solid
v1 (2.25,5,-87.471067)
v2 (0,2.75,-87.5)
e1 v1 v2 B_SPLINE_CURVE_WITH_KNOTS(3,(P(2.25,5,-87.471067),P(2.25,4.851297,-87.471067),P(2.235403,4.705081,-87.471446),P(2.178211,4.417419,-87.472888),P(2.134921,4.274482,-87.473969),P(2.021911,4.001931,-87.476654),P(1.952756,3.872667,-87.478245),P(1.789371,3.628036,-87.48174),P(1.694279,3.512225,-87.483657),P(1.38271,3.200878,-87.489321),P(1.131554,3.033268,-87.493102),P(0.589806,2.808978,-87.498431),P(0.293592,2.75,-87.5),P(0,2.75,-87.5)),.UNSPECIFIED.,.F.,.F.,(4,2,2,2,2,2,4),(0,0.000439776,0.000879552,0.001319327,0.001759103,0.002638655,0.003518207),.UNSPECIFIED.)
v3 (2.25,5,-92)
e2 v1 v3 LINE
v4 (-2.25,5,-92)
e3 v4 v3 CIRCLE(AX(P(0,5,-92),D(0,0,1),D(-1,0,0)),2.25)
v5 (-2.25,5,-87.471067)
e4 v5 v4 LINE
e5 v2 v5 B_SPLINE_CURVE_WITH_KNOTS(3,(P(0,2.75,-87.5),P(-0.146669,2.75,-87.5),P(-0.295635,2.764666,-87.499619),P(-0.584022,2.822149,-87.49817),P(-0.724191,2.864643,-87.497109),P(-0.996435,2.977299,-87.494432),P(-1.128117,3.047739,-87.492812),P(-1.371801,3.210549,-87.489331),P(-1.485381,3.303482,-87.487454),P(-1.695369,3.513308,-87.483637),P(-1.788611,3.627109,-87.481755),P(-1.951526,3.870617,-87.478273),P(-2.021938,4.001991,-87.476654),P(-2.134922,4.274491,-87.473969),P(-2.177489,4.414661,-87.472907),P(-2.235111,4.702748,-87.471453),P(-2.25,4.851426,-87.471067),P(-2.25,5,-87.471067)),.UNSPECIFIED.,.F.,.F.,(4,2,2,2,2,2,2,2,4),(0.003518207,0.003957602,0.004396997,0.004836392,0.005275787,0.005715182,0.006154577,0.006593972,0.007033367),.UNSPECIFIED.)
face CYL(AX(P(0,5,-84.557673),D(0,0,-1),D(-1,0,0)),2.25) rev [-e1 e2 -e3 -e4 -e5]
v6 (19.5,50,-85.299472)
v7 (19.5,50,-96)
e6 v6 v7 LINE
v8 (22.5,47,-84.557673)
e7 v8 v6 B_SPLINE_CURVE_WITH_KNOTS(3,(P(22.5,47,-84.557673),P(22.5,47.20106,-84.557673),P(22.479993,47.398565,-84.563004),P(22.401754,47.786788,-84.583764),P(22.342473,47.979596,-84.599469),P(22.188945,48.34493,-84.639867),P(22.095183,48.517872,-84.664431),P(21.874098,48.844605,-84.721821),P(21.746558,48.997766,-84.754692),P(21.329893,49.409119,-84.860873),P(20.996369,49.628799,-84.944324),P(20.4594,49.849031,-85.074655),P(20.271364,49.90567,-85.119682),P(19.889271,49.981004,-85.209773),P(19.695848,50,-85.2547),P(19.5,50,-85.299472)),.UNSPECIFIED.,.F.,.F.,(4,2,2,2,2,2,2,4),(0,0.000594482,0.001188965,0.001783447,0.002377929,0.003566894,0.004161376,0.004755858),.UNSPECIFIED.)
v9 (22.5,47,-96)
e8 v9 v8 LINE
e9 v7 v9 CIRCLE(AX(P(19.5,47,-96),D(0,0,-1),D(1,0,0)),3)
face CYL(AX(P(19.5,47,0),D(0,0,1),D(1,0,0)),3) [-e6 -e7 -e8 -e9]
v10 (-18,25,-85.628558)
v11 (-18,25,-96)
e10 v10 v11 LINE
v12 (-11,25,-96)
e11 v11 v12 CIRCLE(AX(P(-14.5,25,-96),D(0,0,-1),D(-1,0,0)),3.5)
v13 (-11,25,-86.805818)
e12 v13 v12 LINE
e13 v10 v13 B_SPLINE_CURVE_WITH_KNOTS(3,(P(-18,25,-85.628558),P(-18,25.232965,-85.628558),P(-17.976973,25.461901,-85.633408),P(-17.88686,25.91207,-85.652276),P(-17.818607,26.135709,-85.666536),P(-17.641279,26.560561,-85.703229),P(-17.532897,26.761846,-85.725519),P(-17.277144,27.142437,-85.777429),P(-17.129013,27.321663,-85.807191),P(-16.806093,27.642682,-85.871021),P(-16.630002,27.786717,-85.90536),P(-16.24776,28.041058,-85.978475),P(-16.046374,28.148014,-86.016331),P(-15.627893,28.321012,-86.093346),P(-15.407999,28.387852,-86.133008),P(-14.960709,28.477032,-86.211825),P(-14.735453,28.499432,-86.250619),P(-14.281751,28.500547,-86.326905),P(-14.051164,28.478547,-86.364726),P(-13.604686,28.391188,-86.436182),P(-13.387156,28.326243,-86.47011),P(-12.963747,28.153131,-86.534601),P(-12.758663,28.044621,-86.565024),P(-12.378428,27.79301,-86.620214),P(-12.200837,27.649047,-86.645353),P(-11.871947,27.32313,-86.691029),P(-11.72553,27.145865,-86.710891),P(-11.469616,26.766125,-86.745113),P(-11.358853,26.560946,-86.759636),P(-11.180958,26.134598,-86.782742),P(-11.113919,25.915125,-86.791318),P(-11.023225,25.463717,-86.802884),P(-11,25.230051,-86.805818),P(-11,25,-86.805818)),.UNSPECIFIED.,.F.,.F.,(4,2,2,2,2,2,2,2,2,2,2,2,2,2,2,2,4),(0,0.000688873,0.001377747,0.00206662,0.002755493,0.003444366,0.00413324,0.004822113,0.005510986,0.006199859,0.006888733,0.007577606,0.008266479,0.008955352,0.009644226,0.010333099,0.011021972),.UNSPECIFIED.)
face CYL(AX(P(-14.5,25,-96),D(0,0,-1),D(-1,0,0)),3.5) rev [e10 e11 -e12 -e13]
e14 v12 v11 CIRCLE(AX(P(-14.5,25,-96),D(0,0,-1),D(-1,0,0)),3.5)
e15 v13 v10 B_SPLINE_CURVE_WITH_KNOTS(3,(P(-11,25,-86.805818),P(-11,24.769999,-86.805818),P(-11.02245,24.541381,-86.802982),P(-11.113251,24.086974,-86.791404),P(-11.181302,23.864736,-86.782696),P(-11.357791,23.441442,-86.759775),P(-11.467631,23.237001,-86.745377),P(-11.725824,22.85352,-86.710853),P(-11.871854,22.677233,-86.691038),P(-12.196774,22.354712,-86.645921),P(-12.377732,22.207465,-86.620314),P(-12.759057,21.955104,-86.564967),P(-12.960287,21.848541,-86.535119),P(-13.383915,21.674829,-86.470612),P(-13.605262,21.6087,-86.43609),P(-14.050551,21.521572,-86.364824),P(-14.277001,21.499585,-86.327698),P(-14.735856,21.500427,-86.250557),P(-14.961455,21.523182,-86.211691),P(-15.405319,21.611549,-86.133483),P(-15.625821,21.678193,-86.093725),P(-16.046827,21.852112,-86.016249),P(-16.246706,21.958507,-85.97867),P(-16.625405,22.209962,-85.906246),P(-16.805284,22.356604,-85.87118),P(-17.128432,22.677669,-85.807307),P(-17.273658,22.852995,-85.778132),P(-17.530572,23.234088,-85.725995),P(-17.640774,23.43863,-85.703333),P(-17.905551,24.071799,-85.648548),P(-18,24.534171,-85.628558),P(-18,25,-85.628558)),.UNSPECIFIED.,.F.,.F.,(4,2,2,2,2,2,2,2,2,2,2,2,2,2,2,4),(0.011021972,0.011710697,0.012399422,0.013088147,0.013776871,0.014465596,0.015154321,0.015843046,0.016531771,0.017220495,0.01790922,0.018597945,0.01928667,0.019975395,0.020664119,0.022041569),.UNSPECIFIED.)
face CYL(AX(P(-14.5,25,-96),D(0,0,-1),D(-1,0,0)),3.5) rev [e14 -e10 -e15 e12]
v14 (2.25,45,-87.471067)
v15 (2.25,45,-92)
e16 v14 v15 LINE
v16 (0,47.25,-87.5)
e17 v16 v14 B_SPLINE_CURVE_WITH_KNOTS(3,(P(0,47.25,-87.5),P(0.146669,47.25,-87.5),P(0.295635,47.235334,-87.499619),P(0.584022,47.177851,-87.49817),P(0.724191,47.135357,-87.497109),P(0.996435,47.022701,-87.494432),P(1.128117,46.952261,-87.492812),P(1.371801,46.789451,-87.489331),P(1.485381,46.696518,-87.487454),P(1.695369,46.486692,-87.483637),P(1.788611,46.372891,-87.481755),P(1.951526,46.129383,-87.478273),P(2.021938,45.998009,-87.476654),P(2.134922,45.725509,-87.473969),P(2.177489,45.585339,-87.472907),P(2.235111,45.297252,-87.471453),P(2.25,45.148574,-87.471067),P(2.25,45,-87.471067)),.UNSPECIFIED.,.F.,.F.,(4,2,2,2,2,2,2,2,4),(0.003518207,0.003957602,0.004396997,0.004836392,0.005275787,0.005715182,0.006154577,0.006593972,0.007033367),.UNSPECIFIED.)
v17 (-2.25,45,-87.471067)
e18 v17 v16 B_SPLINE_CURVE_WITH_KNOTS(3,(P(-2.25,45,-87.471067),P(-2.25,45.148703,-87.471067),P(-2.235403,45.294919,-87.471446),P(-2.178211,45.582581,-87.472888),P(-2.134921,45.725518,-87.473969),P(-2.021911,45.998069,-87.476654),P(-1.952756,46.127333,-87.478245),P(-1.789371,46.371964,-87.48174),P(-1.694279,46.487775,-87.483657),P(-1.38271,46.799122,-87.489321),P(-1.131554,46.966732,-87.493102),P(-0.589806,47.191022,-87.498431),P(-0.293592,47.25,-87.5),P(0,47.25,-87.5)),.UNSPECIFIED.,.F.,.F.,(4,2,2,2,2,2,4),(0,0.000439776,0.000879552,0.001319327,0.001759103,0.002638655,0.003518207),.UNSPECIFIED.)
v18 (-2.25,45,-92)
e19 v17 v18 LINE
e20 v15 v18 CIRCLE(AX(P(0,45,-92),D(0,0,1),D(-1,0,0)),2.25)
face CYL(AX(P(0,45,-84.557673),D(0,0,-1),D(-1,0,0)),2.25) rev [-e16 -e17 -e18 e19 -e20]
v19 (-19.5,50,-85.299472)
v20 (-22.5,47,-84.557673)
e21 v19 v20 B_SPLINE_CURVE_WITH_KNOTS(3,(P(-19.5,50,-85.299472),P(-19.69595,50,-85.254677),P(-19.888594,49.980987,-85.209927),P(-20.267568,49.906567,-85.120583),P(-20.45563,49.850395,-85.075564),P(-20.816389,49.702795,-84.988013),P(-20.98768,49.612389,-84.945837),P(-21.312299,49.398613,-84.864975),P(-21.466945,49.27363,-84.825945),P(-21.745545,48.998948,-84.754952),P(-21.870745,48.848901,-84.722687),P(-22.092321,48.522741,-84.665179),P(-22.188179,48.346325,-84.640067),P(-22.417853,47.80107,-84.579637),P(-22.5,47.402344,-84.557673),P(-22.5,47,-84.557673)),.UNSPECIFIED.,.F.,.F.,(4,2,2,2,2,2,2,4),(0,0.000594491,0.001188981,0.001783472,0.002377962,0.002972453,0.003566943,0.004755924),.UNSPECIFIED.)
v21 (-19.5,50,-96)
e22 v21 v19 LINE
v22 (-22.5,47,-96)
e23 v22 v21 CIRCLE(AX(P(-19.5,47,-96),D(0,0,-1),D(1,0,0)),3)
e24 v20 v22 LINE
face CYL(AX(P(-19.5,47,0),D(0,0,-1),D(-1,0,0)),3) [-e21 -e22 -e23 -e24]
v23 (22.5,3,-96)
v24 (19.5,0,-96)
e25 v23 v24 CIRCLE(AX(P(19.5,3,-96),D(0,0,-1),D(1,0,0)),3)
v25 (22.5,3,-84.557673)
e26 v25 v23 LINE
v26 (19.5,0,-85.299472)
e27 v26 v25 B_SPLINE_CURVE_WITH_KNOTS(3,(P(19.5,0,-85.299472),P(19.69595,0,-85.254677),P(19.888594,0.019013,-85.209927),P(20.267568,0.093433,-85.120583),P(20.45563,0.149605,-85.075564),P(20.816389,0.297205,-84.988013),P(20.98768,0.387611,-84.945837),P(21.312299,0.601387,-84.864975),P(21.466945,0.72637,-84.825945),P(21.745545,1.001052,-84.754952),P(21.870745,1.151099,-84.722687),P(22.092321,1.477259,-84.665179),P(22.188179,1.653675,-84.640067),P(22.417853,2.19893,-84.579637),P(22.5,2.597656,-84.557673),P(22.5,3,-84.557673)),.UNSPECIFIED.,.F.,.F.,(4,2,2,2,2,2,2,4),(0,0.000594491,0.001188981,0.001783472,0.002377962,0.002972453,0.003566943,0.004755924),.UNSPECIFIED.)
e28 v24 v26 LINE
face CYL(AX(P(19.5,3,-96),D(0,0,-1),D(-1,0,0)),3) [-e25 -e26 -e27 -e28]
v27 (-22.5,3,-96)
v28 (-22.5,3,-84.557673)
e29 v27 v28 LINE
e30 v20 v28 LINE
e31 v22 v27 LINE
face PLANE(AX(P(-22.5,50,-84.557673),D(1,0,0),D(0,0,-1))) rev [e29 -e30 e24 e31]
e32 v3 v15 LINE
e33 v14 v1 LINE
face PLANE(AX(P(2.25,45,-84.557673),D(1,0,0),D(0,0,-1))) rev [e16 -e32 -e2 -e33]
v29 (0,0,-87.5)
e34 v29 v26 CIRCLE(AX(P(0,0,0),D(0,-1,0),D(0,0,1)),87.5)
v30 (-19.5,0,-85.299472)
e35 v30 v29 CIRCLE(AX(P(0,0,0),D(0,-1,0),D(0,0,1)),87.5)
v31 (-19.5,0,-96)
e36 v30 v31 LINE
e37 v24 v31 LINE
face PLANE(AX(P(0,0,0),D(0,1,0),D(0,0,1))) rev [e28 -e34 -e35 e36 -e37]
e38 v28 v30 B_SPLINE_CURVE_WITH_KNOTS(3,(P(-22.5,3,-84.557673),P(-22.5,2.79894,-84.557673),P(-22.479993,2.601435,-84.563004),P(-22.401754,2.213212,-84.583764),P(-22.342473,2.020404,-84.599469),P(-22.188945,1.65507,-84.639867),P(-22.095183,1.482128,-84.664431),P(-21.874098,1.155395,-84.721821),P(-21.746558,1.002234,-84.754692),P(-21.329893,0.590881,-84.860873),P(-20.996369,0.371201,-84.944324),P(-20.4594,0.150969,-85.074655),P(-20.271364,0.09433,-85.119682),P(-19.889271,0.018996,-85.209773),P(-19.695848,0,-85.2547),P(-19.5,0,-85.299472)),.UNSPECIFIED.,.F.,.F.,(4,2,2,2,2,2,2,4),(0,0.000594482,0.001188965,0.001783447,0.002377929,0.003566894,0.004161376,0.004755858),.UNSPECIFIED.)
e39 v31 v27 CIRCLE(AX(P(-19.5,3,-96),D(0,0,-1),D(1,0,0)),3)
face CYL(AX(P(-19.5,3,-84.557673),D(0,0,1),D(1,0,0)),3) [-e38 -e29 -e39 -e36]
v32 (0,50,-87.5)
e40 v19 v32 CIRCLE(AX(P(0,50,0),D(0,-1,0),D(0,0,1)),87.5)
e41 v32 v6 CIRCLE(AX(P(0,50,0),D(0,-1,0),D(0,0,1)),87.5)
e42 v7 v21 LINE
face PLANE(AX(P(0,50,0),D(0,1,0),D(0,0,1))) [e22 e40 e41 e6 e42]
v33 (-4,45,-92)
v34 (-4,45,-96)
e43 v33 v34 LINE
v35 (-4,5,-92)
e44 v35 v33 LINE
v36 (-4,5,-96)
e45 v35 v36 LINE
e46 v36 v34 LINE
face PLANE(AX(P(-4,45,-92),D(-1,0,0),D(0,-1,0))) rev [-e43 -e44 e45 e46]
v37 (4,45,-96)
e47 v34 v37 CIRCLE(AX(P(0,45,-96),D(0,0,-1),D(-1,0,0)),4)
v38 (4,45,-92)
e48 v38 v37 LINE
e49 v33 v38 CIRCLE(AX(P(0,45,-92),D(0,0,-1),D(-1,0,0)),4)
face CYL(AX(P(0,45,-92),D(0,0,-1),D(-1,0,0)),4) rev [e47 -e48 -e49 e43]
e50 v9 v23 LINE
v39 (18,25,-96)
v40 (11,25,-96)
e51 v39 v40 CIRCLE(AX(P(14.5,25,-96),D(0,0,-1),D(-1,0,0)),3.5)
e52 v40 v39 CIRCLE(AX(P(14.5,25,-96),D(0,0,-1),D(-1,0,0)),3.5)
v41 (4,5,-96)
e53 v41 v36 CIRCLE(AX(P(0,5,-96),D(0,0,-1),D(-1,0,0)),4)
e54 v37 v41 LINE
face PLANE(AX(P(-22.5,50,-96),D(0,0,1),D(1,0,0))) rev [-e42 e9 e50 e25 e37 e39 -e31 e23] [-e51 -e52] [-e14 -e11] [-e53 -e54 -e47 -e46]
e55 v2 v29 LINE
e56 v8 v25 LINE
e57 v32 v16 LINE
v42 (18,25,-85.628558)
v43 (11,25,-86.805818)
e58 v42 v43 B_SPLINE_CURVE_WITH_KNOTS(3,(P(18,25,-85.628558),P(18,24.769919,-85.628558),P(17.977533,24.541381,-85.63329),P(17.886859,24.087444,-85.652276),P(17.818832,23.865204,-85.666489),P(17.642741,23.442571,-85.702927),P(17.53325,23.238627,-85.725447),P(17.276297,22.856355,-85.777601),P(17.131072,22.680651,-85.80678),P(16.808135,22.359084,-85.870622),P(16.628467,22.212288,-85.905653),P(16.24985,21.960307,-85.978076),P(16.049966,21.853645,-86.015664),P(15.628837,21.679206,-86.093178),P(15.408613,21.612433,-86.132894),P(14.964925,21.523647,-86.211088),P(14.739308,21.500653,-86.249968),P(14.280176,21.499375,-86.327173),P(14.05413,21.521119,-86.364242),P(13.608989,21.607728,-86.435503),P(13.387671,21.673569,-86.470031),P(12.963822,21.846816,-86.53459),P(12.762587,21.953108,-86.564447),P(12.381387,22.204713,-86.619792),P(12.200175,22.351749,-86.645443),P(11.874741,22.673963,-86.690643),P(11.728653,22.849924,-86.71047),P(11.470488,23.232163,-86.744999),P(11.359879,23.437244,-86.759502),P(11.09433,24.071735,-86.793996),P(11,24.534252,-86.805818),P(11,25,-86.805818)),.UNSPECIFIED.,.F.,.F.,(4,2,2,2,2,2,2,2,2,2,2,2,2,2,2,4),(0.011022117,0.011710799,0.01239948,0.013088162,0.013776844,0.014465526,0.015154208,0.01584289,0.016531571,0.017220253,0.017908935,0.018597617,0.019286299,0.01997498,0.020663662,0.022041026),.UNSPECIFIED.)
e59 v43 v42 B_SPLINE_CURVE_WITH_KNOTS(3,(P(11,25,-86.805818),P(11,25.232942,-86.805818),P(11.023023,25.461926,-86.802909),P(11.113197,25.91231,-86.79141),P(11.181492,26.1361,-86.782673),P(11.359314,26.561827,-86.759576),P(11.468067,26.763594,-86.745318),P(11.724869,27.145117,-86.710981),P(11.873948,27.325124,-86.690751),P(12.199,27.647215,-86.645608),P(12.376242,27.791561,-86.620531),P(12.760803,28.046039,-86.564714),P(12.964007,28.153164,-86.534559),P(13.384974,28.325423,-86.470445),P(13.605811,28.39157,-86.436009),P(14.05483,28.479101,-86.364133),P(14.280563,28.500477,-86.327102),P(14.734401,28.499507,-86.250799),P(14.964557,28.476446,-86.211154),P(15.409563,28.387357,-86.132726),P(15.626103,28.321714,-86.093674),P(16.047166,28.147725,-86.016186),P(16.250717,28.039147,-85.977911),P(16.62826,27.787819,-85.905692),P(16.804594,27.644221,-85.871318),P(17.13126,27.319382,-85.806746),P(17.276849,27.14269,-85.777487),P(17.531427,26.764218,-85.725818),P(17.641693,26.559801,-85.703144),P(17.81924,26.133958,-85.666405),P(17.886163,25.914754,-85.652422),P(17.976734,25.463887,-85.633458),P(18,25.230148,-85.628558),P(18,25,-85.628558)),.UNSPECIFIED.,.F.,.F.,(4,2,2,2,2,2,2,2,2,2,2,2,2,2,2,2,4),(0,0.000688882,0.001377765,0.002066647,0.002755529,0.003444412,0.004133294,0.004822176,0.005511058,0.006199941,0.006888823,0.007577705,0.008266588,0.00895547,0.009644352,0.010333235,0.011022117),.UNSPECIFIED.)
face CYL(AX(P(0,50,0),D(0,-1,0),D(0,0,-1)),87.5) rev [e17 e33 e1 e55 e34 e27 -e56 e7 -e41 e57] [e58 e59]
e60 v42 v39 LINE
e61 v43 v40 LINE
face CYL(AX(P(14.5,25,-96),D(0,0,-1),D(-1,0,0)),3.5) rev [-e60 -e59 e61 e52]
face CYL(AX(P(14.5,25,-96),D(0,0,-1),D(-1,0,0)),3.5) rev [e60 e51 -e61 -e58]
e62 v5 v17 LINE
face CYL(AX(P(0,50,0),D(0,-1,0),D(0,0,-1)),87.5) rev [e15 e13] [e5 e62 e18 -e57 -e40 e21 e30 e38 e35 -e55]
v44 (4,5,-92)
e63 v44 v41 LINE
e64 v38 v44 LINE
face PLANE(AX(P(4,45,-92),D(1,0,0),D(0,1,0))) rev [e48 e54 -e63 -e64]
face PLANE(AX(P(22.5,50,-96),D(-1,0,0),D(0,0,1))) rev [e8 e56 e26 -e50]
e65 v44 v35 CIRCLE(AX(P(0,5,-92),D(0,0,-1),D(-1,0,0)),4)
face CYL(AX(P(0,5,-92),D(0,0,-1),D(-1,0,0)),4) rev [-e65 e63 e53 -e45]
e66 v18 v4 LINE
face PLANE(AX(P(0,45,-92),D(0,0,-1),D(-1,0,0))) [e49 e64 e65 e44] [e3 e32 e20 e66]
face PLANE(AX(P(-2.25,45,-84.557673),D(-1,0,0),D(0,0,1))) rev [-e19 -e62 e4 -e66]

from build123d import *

# Parameters (mm, degrees)
BOSS_EXTRUDE1_DEPTH   = 50
M8X1_0_TAPPED_HOLE1_D = 7
CUT_EXTRUDE1_DEPTH    = 57.010506805
CUT_EXTRUDE2_DEPTH    = 4
FILLET1_R             = 3


with BuildPart() as part:
    # Sketch1 → Boss-Extrude1 (new body)
    with BuildSketch(Plane(origin=(0, 0, 0), x_dir=(1, 0, 0), z_dir=(0, 1, 0))):
        with BuildLine():
            Line((-22.5, 84.557672626), (-22.5, 96))
            Line((-22.5, 96), (22.5, 96))
            Line((22.5, 96), (22.5, 84.557672626))
            ThreePointArc((22.5, 84.557672626), (0, 87.5), (-22.5, 84.557672626))
        make_face()
    extrude(amount=BOSS_EXTRUDE1_DEPTH)

    # M8x1.0 Tapped Hole1 (through all)
    with Locations(Plane(origin=(0, 0, -96), x_dir=(-1, 0, 0), z_dir=(0, 0, -1))):
        with Locations((-14.5, 25), (14.5, 25)):
            Hole(M8X1_0_TAPPED_HOLE1_D / 2)

    # Sketch4 → Cut-Extrude1 (cut, through all)
    with BuildSketch(Plane(origin=(0, 0, -96), x_dir=(-1, 0, 0), z_dir=(0, 0, -1))):
        with BuildLine():
            Line((2.25, 45), (2.25, 5))
            ThreePointArc((2.25, 5), (0, 2.75), (-2.25, 5))
            Line((-2.25, 5), (-2.25, 45))
            ThreePointArc((-2.25, 45), (0, 47.25), (2.25, 45))
        make_face()
    extrude(amount=-CUT_EXTRUDE1_DEPTH, mode=Mode.SUBTRACT)

    # Sketch5 → Cut-Extrude2 (cut)
    with BuildSketch(Plane(origin=(0, 0, -96), x_dir=(-1, 0, 0), z_dir=(0, 0, -1))):
        with BuildLine():
            Line((4, 45), (4, 5))
            ThreePointArc((4, 5), (0, 1), (-4, 5))
            Line((-4, 5), (-4, 45))
            ThreePointArc((-4, 45), (0, 49), (4, 45))
        make_face()
    extrude(amount=-CUT_EXTRUDE2_DEPTH, mode=Mode.SUBTRACT)

    # Fillet1
    fillet1_edges = [part.edges().sort_by_distance(p)[0] for p in [
        (22.5, 50, -90.278836313),
        (22.5, 0, -90.278836313),
        (-22.5, 0, -90.278836313),
        (-22.5, 50, -90.278836313),
    ]]
    fillet(fillet1_edges, radius=FILLET1_R)


solid = part.part
